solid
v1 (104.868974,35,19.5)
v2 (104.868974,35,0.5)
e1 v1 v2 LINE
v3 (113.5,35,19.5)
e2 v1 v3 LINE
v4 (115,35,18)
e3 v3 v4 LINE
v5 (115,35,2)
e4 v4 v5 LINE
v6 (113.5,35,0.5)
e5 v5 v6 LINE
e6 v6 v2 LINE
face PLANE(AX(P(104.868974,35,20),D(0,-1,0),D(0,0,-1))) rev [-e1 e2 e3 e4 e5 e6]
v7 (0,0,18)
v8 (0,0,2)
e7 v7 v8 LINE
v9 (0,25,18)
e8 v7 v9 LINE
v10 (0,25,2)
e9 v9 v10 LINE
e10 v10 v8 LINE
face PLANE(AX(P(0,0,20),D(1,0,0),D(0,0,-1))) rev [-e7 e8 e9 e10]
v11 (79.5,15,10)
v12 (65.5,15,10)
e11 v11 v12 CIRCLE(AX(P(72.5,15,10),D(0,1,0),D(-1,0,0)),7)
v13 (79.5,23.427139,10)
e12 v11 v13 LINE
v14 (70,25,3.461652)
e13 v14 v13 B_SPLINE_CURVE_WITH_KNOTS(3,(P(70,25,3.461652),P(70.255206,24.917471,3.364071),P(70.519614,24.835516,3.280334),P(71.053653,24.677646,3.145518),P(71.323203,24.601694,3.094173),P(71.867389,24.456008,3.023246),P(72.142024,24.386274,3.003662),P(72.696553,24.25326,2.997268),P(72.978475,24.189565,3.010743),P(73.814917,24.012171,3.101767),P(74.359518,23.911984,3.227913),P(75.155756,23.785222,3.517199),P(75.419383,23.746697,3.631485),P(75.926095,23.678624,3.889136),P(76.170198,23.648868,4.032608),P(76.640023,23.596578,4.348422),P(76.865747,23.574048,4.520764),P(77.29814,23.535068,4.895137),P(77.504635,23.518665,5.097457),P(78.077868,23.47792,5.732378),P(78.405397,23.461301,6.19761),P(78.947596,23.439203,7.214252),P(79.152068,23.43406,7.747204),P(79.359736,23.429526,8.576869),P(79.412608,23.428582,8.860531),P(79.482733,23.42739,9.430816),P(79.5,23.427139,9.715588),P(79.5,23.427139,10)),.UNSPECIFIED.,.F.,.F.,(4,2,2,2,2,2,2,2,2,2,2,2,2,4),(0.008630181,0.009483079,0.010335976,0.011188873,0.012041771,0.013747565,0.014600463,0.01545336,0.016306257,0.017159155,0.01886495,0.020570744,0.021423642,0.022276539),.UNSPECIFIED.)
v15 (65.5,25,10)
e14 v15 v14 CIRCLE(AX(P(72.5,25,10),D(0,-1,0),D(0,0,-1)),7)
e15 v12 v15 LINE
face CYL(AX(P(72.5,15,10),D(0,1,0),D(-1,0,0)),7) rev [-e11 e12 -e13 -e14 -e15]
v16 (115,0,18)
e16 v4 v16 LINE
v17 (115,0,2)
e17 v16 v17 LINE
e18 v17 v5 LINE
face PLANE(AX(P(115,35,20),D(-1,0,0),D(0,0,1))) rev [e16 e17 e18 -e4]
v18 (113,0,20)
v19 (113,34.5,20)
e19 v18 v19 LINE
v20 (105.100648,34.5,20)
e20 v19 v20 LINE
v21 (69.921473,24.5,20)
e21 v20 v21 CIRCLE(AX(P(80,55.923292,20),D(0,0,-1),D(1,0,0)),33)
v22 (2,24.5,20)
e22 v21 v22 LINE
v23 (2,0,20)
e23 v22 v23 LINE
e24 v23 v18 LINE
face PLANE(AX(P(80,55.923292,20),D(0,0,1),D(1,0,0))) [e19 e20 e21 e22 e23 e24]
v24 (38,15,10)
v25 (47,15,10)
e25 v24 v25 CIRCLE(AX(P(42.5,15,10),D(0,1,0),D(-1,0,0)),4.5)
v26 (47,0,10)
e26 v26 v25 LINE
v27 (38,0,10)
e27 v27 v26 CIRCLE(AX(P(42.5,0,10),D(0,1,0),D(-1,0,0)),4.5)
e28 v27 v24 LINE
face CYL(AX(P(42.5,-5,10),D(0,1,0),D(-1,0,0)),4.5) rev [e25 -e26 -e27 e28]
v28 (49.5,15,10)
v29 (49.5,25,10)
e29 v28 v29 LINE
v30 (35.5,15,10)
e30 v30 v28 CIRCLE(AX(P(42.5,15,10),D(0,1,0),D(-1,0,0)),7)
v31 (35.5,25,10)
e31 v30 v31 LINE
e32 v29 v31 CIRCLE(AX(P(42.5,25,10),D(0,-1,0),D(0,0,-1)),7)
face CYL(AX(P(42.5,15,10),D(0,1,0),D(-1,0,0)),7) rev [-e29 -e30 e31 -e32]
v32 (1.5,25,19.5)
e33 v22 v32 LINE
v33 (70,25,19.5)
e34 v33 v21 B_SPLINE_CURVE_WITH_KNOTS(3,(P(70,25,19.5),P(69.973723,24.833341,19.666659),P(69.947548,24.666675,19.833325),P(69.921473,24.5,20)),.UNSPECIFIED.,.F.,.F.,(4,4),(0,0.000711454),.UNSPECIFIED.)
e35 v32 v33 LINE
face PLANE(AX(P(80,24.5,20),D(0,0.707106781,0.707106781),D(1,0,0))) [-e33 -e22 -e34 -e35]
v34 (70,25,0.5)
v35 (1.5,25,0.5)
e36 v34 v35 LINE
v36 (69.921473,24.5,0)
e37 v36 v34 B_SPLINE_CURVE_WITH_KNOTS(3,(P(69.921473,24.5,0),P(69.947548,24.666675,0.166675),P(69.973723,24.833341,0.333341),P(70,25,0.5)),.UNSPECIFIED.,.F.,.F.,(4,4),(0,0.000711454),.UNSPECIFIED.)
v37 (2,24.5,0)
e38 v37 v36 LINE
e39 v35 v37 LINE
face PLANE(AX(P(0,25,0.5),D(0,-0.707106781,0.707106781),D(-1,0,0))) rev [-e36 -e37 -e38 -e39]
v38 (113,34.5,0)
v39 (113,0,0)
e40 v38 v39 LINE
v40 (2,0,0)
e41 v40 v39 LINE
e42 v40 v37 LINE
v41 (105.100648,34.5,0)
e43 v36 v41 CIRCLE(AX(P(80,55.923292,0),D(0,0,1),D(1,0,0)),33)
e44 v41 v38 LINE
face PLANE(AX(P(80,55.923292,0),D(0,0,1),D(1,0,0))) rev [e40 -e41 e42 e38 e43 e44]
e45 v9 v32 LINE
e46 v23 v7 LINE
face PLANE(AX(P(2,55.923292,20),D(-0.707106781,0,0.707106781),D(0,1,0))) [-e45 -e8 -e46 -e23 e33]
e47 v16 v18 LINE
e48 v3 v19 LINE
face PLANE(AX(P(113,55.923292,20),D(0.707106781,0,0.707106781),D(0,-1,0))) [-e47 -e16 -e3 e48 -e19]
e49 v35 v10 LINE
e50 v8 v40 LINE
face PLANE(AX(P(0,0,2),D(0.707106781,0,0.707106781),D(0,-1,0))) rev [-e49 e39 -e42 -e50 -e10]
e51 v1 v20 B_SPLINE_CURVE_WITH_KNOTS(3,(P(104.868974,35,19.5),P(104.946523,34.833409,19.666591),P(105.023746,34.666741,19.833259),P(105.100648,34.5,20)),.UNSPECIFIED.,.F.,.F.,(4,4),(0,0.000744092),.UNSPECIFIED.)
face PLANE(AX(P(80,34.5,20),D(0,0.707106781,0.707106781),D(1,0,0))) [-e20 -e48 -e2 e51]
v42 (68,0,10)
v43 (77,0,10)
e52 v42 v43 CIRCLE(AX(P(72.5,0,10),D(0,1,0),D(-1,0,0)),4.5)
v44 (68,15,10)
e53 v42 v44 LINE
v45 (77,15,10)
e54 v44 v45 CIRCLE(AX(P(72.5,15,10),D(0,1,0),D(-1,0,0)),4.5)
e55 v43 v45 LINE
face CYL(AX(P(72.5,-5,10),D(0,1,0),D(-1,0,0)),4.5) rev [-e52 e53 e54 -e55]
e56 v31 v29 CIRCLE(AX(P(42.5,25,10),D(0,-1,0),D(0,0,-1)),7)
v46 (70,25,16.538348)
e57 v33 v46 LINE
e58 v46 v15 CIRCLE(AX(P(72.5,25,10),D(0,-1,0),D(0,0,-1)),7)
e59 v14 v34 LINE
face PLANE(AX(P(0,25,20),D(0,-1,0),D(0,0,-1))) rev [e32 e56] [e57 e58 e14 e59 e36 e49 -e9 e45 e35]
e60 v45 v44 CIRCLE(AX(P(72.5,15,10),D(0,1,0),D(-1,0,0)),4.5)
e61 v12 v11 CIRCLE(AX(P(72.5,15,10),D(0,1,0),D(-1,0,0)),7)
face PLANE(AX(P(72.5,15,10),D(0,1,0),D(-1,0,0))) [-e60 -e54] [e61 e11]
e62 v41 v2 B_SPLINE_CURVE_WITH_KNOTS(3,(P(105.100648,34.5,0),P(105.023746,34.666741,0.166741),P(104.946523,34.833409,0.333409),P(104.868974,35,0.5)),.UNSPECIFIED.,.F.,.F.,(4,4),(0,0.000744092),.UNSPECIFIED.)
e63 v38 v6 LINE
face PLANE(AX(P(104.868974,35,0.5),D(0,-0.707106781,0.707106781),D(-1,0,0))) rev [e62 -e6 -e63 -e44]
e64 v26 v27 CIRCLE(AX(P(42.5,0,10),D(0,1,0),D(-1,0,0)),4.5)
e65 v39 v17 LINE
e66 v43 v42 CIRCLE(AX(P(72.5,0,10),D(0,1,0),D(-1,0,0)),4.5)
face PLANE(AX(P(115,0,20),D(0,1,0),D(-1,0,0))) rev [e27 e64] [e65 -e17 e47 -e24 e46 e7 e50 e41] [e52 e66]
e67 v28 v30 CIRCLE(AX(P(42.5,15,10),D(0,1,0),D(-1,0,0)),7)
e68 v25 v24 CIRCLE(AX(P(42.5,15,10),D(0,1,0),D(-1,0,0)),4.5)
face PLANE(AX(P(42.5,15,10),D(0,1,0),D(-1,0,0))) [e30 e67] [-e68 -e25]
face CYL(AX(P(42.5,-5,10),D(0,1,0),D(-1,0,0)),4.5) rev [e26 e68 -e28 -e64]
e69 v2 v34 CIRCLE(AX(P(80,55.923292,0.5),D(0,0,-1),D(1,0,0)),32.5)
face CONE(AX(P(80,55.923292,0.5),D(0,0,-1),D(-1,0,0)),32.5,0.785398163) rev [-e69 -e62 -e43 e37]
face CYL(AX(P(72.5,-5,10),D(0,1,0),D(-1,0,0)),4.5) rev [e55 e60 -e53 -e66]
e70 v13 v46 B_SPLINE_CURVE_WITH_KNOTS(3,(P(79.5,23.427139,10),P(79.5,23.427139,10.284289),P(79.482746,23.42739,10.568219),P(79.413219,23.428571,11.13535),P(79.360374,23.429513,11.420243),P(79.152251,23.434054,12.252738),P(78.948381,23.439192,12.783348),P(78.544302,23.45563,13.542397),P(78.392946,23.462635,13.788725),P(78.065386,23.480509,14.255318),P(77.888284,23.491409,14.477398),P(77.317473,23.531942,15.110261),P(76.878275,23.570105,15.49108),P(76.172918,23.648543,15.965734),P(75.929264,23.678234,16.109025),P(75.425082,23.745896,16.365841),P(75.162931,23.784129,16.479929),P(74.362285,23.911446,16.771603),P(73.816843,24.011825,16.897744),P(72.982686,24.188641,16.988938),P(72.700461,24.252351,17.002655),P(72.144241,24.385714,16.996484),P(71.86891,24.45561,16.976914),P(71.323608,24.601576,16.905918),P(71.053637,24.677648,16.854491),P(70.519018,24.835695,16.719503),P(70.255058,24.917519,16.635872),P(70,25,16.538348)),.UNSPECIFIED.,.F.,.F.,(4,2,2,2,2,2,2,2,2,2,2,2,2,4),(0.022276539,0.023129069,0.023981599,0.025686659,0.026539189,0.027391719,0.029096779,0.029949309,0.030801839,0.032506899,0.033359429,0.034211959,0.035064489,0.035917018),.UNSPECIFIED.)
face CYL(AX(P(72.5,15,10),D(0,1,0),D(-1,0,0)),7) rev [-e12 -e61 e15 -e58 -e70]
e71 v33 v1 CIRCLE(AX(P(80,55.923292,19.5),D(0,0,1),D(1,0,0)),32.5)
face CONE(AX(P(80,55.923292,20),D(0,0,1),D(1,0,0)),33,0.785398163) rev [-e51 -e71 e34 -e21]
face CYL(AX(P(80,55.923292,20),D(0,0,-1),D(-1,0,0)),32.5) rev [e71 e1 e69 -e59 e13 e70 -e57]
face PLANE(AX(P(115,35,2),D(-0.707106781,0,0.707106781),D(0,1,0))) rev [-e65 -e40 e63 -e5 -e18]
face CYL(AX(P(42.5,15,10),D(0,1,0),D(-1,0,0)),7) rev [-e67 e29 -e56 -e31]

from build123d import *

# Parameters (mm, degrees)
EXTRUDE_1_DEPTH     = 20
SKETCH_4_R          = 7
CUT_EXTRUDE_1_DEPTH = 20
SKETCH_5_R          = 4.5
CUT_EXTRUDE_2_DEPTH = 20
CHAMFER_1_SIZE      = 2
CHAMFER_2_SIZE      = 0.5


with BuildPart() as part:
    # 草图2 → 凸台-拉伸1 (new body)
    with BuildSketch(Plane.XY):
        with BuildLine():
            Line((0, 0), (0, 25))
            Line((0, 25), (70, 25))
            ThreePointArc((70, 25), (88.959441577, 24.682639084), (104.868973518, 35))
            Line((104.868973518, 35), (115, 35))
            Line((115, 35), (115, 0))
            Line((115, 0), (0, 0))
        make_face()
    extrude(amount=EXTRUDE_1_DEPTH)

    # 草图4 → 切除-拉伸1 (cut)
    with BuildSketch(Plane(origin=(0, 35, 0), x_dir=(1, 0, 0), z_dir=(0, 1, 0))):
        with Locations(Location((42.5, -10, 0), (0, 0, 180))):
            Circle(SKETCH_4_R)
        with Locations(Location((72.5, -10, 0), (0, 0, 180))):
            Circle(SKETCH_4_R)
    extrude(amount=-CUT_EXTRUDE_1_DEPTH, mode=Mode.SUBTRACT)

    # 草图5 → 切除-拉伸2 (cut)
    with BuildSketch(Plane(origin=(0, 15, 0), x_dir=(1, 0, 0), z_dir=(0, 1, 0))):
        with Locations(Location((42.5, -10, 0), (0, 0, 180))):
            Circle(SKETCH_5_R)
        with Locations(Location((72.5, -10, 0), (0, 0, 180))):
            Circle(SKETCH_5_R)
    extrude(amount=-CUT_EXTRUDE_2_DEPTH, mode=Mode.SUBTRACT)

    # 倒角1
    chamfer_1_edges = [part.edges().sort_by_distance(p)[0] for p in [
        (0, 12.5, 20),
        (0, 12.5, 0),
        (115, 17.5, 20),
        (115, 17.5, 0),
    ]]
    chamfer(chamfer_1_edges, length=CHAMFER_1_SIZE)

    # 倒角2
    chamfer_2_edges = [part.edges().sort_by_distance(p)[0] for p in [
        (88.959441577, 24.682639084, 20),
        (36, 25, 20),
        (108.934486759, 35, 20),
        (108.934486759, 35, 0),
        (36, 25, 0),
        (88.959441577, 24.682639084, 0),
    ]]
    chamfer(chamfer_2_edges, length=CHAMFER_2_SIZE)


solid = part.part
